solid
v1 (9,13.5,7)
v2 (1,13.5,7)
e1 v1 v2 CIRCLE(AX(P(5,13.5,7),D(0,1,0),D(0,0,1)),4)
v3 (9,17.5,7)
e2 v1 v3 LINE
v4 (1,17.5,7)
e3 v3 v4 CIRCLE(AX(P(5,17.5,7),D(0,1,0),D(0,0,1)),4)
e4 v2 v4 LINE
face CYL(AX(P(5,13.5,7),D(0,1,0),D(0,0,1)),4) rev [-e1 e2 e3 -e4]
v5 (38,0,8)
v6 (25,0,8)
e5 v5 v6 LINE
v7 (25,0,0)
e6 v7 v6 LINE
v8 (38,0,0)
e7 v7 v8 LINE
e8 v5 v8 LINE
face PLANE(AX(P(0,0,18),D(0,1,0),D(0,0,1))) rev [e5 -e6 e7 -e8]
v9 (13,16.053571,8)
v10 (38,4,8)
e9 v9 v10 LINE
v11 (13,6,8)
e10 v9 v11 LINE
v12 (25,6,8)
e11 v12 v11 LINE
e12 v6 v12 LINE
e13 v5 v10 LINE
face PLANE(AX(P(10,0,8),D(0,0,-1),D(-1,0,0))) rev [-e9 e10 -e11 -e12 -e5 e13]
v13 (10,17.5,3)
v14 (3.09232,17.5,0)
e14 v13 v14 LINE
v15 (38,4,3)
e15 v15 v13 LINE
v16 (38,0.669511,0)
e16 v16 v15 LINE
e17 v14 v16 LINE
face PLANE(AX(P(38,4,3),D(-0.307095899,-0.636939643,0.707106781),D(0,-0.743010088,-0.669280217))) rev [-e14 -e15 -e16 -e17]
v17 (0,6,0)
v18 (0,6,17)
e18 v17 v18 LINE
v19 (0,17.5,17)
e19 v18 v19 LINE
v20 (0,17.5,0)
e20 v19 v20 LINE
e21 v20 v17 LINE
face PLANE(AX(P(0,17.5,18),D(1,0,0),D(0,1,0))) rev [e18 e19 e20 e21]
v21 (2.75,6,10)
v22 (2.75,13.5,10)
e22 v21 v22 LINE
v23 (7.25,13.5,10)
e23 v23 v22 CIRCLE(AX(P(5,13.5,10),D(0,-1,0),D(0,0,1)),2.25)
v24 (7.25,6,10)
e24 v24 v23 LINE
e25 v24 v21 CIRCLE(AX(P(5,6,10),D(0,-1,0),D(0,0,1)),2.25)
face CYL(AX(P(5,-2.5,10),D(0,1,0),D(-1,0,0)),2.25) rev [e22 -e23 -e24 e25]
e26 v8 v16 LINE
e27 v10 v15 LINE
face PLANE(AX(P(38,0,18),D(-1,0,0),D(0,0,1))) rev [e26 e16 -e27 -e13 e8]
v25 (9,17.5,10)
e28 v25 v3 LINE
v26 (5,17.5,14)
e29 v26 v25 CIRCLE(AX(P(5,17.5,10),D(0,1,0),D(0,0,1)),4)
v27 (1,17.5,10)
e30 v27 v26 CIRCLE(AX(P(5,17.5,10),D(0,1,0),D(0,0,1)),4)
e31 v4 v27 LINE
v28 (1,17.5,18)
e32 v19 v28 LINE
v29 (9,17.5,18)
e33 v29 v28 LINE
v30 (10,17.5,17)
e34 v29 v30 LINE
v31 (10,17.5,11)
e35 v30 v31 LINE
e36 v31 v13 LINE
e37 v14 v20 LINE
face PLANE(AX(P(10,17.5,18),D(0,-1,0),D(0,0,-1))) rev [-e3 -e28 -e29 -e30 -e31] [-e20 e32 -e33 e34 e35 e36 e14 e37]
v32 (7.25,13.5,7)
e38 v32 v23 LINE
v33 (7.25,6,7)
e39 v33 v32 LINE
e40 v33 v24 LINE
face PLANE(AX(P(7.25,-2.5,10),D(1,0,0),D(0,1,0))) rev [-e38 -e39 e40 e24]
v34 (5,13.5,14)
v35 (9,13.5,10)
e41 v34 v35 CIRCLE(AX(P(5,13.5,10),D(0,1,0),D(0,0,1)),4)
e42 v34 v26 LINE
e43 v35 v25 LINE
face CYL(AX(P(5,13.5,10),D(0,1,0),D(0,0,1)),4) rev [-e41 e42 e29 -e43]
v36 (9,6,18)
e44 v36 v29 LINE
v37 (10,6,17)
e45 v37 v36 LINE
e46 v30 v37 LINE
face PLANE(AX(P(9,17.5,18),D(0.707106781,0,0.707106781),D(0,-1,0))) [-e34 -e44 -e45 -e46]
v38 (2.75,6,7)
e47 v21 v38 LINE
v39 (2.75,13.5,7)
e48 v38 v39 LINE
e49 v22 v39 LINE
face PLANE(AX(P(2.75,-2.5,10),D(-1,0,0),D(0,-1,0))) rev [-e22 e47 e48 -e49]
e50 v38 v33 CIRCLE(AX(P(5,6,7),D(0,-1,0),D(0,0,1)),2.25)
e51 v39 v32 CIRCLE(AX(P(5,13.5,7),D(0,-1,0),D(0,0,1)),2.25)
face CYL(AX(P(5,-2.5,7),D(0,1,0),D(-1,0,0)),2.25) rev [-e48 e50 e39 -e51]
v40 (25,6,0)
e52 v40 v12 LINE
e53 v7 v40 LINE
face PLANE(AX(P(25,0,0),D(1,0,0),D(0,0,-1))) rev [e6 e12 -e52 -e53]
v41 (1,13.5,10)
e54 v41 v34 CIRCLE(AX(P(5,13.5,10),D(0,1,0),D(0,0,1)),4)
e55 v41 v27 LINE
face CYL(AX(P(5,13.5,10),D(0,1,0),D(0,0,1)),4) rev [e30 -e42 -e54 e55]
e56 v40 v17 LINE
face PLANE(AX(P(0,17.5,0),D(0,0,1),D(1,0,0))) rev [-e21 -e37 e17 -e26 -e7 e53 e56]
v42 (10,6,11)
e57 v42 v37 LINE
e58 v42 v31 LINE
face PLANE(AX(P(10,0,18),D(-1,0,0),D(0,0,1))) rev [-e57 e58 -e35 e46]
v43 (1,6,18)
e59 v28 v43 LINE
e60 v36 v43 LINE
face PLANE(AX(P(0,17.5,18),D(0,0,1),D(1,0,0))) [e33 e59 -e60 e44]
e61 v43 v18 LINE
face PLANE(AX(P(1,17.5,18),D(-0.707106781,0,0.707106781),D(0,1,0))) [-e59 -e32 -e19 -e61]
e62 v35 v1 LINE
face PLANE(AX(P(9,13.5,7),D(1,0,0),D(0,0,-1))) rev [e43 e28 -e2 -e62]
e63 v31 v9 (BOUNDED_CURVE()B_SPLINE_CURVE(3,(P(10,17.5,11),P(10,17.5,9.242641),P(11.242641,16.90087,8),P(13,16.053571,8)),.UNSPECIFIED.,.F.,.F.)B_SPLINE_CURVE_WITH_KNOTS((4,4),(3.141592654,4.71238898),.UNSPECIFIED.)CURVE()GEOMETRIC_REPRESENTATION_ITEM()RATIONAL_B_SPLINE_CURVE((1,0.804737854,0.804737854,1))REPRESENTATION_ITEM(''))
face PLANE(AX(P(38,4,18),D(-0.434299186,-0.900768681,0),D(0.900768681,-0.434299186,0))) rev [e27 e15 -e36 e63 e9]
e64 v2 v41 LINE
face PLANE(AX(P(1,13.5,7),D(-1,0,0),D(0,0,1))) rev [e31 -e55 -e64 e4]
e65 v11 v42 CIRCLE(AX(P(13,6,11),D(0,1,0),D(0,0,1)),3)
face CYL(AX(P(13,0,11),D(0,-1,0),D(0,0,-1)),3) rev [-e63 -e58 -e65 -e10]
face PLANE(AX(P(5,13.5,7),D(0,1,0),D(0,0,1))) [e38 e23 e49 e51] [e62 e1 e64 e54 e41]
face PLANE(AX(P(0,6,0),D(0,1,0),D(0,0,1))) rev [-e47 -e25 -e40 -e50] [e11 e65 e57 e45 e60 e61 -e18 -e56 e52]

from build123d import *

# Parameters (mm, degrees)
BOSS_EXTRUDE1_DEPTH = 18
CHAMFER1_SIZE       = 3
CUT_EXTRUDE1_DEPTH  = 20
CUT_EXTRUDE3_DEPTH  = 4
SKETCH3_W           = 25
SKETCH3_H           = 6
CUT_EXTRUDE2_DEPTH  = 46.543934832
SKETCH5_W           = 28
SKETCH5_H           = 10
CUT_EXTRUDE4_DEPTH  = 46.543934832
FILLET1_R           = 3
CHAMFER2_SIZE       = 1


with BuildPart() as part:
    # Sketch1 → Boss-Extrude1 (new body)
    with BuildSketch(Plane.XY):
        Polygon((0, 17.5), (0, 0), (38, 0), (38, 4), (10, 17.5), align=None)
    extrude(amount=BOSS_EXTRUDE1_DEPTH)

    # Chamfer1
    chamfer1_edges = [part.edges().sort_by_distance(p)[0] for p in [
        (24, 10.75, 0),
    ]]
    chamfer(chamfer1_edges, length=CHAMFER1_SIZE)

    # Sketch2 → Cut-Extrude1 (cut)
    with BuildSketch(Plane(origin=(0, 17.5, 0), x_dir=(1, 0, 0), z_dir=(0, 1, 0))):
        with BuildLine():
            Line((2.75, -10), (2.75, -7))
            ThreePointArc((2.75, -7), (5, -4.75), (7.25, -7))
            Line((7.25, -7), (7.25, -10))
            ThreePointArc((7.25, -10), (5, -12.25), (2.75, -10))
        make_face()
    extrude(amount=-CUT_EXTRUDE1_DEPTH, mode=Mode.SUBTRACT)

    # Sketch4 → Cut-Extrude3 (cut)
    with BuildSketch(Plane(origin=(0, 17.5, 0), x_dir=(1, 0, 0), z_dir=(0, 1, 0))):
        with BuildLine():
            Line((9, -7), (9, -10))
            ThreePointArc((9, -10), (5, -14), (1, -10))
            Line((1, -10), (1, -7))
            ThreePointArc((1, -7), (5, -3), (9, -7))
        make_face()
    extrude(amount=-CUT_EXTRUDE3_DEPTH, mode=Mode.SUBTRACT)

    # Sketch3 → Cut-Extrude2 (cut, through all)
    with BuildSketch(Plane.XY.offset(18)):
        with Locations((12.5, 3)):
            Rectangle(SKETCH3_W, SKETCH3_H)
    extrude(amount=-CUT_EXTRUDE2_DEPTH, mode=Mode.SUBTRACT)

    # Sketch5 → Cut-Extrude4 (cut, through all)
    with BuildSketch(Plane(origin=(0, 17.5, 0), x_dir=(1, 0, 0), z_dir=(0, 1, 0))):
        with Locations((24, -13)):
            Rectangle(SKETCH5_W, SKETCH5_H)
    extrude(amount=-CUT_EXTRUDE4_DEPTH, mode=Mode.SUBTRACT)

    # Fillet1
    fillet1_edges = [part.edges().sort_by_distance(p)[0] for p in [
        (10, 11.75, 8),
    ]]
    fillet(fillet1_edges, radius=FILLET1_R)

    # Chamfer2
    chamfer2_edges = [part.edges().sort_by_distance(p)[0] for p in [
        (10, 11.75, 18),
        (0, 11.75, 18),
    ]]
    chamfer(chamfer2_edges, length=CHAMFER2_SIZE)


solid = part.part
